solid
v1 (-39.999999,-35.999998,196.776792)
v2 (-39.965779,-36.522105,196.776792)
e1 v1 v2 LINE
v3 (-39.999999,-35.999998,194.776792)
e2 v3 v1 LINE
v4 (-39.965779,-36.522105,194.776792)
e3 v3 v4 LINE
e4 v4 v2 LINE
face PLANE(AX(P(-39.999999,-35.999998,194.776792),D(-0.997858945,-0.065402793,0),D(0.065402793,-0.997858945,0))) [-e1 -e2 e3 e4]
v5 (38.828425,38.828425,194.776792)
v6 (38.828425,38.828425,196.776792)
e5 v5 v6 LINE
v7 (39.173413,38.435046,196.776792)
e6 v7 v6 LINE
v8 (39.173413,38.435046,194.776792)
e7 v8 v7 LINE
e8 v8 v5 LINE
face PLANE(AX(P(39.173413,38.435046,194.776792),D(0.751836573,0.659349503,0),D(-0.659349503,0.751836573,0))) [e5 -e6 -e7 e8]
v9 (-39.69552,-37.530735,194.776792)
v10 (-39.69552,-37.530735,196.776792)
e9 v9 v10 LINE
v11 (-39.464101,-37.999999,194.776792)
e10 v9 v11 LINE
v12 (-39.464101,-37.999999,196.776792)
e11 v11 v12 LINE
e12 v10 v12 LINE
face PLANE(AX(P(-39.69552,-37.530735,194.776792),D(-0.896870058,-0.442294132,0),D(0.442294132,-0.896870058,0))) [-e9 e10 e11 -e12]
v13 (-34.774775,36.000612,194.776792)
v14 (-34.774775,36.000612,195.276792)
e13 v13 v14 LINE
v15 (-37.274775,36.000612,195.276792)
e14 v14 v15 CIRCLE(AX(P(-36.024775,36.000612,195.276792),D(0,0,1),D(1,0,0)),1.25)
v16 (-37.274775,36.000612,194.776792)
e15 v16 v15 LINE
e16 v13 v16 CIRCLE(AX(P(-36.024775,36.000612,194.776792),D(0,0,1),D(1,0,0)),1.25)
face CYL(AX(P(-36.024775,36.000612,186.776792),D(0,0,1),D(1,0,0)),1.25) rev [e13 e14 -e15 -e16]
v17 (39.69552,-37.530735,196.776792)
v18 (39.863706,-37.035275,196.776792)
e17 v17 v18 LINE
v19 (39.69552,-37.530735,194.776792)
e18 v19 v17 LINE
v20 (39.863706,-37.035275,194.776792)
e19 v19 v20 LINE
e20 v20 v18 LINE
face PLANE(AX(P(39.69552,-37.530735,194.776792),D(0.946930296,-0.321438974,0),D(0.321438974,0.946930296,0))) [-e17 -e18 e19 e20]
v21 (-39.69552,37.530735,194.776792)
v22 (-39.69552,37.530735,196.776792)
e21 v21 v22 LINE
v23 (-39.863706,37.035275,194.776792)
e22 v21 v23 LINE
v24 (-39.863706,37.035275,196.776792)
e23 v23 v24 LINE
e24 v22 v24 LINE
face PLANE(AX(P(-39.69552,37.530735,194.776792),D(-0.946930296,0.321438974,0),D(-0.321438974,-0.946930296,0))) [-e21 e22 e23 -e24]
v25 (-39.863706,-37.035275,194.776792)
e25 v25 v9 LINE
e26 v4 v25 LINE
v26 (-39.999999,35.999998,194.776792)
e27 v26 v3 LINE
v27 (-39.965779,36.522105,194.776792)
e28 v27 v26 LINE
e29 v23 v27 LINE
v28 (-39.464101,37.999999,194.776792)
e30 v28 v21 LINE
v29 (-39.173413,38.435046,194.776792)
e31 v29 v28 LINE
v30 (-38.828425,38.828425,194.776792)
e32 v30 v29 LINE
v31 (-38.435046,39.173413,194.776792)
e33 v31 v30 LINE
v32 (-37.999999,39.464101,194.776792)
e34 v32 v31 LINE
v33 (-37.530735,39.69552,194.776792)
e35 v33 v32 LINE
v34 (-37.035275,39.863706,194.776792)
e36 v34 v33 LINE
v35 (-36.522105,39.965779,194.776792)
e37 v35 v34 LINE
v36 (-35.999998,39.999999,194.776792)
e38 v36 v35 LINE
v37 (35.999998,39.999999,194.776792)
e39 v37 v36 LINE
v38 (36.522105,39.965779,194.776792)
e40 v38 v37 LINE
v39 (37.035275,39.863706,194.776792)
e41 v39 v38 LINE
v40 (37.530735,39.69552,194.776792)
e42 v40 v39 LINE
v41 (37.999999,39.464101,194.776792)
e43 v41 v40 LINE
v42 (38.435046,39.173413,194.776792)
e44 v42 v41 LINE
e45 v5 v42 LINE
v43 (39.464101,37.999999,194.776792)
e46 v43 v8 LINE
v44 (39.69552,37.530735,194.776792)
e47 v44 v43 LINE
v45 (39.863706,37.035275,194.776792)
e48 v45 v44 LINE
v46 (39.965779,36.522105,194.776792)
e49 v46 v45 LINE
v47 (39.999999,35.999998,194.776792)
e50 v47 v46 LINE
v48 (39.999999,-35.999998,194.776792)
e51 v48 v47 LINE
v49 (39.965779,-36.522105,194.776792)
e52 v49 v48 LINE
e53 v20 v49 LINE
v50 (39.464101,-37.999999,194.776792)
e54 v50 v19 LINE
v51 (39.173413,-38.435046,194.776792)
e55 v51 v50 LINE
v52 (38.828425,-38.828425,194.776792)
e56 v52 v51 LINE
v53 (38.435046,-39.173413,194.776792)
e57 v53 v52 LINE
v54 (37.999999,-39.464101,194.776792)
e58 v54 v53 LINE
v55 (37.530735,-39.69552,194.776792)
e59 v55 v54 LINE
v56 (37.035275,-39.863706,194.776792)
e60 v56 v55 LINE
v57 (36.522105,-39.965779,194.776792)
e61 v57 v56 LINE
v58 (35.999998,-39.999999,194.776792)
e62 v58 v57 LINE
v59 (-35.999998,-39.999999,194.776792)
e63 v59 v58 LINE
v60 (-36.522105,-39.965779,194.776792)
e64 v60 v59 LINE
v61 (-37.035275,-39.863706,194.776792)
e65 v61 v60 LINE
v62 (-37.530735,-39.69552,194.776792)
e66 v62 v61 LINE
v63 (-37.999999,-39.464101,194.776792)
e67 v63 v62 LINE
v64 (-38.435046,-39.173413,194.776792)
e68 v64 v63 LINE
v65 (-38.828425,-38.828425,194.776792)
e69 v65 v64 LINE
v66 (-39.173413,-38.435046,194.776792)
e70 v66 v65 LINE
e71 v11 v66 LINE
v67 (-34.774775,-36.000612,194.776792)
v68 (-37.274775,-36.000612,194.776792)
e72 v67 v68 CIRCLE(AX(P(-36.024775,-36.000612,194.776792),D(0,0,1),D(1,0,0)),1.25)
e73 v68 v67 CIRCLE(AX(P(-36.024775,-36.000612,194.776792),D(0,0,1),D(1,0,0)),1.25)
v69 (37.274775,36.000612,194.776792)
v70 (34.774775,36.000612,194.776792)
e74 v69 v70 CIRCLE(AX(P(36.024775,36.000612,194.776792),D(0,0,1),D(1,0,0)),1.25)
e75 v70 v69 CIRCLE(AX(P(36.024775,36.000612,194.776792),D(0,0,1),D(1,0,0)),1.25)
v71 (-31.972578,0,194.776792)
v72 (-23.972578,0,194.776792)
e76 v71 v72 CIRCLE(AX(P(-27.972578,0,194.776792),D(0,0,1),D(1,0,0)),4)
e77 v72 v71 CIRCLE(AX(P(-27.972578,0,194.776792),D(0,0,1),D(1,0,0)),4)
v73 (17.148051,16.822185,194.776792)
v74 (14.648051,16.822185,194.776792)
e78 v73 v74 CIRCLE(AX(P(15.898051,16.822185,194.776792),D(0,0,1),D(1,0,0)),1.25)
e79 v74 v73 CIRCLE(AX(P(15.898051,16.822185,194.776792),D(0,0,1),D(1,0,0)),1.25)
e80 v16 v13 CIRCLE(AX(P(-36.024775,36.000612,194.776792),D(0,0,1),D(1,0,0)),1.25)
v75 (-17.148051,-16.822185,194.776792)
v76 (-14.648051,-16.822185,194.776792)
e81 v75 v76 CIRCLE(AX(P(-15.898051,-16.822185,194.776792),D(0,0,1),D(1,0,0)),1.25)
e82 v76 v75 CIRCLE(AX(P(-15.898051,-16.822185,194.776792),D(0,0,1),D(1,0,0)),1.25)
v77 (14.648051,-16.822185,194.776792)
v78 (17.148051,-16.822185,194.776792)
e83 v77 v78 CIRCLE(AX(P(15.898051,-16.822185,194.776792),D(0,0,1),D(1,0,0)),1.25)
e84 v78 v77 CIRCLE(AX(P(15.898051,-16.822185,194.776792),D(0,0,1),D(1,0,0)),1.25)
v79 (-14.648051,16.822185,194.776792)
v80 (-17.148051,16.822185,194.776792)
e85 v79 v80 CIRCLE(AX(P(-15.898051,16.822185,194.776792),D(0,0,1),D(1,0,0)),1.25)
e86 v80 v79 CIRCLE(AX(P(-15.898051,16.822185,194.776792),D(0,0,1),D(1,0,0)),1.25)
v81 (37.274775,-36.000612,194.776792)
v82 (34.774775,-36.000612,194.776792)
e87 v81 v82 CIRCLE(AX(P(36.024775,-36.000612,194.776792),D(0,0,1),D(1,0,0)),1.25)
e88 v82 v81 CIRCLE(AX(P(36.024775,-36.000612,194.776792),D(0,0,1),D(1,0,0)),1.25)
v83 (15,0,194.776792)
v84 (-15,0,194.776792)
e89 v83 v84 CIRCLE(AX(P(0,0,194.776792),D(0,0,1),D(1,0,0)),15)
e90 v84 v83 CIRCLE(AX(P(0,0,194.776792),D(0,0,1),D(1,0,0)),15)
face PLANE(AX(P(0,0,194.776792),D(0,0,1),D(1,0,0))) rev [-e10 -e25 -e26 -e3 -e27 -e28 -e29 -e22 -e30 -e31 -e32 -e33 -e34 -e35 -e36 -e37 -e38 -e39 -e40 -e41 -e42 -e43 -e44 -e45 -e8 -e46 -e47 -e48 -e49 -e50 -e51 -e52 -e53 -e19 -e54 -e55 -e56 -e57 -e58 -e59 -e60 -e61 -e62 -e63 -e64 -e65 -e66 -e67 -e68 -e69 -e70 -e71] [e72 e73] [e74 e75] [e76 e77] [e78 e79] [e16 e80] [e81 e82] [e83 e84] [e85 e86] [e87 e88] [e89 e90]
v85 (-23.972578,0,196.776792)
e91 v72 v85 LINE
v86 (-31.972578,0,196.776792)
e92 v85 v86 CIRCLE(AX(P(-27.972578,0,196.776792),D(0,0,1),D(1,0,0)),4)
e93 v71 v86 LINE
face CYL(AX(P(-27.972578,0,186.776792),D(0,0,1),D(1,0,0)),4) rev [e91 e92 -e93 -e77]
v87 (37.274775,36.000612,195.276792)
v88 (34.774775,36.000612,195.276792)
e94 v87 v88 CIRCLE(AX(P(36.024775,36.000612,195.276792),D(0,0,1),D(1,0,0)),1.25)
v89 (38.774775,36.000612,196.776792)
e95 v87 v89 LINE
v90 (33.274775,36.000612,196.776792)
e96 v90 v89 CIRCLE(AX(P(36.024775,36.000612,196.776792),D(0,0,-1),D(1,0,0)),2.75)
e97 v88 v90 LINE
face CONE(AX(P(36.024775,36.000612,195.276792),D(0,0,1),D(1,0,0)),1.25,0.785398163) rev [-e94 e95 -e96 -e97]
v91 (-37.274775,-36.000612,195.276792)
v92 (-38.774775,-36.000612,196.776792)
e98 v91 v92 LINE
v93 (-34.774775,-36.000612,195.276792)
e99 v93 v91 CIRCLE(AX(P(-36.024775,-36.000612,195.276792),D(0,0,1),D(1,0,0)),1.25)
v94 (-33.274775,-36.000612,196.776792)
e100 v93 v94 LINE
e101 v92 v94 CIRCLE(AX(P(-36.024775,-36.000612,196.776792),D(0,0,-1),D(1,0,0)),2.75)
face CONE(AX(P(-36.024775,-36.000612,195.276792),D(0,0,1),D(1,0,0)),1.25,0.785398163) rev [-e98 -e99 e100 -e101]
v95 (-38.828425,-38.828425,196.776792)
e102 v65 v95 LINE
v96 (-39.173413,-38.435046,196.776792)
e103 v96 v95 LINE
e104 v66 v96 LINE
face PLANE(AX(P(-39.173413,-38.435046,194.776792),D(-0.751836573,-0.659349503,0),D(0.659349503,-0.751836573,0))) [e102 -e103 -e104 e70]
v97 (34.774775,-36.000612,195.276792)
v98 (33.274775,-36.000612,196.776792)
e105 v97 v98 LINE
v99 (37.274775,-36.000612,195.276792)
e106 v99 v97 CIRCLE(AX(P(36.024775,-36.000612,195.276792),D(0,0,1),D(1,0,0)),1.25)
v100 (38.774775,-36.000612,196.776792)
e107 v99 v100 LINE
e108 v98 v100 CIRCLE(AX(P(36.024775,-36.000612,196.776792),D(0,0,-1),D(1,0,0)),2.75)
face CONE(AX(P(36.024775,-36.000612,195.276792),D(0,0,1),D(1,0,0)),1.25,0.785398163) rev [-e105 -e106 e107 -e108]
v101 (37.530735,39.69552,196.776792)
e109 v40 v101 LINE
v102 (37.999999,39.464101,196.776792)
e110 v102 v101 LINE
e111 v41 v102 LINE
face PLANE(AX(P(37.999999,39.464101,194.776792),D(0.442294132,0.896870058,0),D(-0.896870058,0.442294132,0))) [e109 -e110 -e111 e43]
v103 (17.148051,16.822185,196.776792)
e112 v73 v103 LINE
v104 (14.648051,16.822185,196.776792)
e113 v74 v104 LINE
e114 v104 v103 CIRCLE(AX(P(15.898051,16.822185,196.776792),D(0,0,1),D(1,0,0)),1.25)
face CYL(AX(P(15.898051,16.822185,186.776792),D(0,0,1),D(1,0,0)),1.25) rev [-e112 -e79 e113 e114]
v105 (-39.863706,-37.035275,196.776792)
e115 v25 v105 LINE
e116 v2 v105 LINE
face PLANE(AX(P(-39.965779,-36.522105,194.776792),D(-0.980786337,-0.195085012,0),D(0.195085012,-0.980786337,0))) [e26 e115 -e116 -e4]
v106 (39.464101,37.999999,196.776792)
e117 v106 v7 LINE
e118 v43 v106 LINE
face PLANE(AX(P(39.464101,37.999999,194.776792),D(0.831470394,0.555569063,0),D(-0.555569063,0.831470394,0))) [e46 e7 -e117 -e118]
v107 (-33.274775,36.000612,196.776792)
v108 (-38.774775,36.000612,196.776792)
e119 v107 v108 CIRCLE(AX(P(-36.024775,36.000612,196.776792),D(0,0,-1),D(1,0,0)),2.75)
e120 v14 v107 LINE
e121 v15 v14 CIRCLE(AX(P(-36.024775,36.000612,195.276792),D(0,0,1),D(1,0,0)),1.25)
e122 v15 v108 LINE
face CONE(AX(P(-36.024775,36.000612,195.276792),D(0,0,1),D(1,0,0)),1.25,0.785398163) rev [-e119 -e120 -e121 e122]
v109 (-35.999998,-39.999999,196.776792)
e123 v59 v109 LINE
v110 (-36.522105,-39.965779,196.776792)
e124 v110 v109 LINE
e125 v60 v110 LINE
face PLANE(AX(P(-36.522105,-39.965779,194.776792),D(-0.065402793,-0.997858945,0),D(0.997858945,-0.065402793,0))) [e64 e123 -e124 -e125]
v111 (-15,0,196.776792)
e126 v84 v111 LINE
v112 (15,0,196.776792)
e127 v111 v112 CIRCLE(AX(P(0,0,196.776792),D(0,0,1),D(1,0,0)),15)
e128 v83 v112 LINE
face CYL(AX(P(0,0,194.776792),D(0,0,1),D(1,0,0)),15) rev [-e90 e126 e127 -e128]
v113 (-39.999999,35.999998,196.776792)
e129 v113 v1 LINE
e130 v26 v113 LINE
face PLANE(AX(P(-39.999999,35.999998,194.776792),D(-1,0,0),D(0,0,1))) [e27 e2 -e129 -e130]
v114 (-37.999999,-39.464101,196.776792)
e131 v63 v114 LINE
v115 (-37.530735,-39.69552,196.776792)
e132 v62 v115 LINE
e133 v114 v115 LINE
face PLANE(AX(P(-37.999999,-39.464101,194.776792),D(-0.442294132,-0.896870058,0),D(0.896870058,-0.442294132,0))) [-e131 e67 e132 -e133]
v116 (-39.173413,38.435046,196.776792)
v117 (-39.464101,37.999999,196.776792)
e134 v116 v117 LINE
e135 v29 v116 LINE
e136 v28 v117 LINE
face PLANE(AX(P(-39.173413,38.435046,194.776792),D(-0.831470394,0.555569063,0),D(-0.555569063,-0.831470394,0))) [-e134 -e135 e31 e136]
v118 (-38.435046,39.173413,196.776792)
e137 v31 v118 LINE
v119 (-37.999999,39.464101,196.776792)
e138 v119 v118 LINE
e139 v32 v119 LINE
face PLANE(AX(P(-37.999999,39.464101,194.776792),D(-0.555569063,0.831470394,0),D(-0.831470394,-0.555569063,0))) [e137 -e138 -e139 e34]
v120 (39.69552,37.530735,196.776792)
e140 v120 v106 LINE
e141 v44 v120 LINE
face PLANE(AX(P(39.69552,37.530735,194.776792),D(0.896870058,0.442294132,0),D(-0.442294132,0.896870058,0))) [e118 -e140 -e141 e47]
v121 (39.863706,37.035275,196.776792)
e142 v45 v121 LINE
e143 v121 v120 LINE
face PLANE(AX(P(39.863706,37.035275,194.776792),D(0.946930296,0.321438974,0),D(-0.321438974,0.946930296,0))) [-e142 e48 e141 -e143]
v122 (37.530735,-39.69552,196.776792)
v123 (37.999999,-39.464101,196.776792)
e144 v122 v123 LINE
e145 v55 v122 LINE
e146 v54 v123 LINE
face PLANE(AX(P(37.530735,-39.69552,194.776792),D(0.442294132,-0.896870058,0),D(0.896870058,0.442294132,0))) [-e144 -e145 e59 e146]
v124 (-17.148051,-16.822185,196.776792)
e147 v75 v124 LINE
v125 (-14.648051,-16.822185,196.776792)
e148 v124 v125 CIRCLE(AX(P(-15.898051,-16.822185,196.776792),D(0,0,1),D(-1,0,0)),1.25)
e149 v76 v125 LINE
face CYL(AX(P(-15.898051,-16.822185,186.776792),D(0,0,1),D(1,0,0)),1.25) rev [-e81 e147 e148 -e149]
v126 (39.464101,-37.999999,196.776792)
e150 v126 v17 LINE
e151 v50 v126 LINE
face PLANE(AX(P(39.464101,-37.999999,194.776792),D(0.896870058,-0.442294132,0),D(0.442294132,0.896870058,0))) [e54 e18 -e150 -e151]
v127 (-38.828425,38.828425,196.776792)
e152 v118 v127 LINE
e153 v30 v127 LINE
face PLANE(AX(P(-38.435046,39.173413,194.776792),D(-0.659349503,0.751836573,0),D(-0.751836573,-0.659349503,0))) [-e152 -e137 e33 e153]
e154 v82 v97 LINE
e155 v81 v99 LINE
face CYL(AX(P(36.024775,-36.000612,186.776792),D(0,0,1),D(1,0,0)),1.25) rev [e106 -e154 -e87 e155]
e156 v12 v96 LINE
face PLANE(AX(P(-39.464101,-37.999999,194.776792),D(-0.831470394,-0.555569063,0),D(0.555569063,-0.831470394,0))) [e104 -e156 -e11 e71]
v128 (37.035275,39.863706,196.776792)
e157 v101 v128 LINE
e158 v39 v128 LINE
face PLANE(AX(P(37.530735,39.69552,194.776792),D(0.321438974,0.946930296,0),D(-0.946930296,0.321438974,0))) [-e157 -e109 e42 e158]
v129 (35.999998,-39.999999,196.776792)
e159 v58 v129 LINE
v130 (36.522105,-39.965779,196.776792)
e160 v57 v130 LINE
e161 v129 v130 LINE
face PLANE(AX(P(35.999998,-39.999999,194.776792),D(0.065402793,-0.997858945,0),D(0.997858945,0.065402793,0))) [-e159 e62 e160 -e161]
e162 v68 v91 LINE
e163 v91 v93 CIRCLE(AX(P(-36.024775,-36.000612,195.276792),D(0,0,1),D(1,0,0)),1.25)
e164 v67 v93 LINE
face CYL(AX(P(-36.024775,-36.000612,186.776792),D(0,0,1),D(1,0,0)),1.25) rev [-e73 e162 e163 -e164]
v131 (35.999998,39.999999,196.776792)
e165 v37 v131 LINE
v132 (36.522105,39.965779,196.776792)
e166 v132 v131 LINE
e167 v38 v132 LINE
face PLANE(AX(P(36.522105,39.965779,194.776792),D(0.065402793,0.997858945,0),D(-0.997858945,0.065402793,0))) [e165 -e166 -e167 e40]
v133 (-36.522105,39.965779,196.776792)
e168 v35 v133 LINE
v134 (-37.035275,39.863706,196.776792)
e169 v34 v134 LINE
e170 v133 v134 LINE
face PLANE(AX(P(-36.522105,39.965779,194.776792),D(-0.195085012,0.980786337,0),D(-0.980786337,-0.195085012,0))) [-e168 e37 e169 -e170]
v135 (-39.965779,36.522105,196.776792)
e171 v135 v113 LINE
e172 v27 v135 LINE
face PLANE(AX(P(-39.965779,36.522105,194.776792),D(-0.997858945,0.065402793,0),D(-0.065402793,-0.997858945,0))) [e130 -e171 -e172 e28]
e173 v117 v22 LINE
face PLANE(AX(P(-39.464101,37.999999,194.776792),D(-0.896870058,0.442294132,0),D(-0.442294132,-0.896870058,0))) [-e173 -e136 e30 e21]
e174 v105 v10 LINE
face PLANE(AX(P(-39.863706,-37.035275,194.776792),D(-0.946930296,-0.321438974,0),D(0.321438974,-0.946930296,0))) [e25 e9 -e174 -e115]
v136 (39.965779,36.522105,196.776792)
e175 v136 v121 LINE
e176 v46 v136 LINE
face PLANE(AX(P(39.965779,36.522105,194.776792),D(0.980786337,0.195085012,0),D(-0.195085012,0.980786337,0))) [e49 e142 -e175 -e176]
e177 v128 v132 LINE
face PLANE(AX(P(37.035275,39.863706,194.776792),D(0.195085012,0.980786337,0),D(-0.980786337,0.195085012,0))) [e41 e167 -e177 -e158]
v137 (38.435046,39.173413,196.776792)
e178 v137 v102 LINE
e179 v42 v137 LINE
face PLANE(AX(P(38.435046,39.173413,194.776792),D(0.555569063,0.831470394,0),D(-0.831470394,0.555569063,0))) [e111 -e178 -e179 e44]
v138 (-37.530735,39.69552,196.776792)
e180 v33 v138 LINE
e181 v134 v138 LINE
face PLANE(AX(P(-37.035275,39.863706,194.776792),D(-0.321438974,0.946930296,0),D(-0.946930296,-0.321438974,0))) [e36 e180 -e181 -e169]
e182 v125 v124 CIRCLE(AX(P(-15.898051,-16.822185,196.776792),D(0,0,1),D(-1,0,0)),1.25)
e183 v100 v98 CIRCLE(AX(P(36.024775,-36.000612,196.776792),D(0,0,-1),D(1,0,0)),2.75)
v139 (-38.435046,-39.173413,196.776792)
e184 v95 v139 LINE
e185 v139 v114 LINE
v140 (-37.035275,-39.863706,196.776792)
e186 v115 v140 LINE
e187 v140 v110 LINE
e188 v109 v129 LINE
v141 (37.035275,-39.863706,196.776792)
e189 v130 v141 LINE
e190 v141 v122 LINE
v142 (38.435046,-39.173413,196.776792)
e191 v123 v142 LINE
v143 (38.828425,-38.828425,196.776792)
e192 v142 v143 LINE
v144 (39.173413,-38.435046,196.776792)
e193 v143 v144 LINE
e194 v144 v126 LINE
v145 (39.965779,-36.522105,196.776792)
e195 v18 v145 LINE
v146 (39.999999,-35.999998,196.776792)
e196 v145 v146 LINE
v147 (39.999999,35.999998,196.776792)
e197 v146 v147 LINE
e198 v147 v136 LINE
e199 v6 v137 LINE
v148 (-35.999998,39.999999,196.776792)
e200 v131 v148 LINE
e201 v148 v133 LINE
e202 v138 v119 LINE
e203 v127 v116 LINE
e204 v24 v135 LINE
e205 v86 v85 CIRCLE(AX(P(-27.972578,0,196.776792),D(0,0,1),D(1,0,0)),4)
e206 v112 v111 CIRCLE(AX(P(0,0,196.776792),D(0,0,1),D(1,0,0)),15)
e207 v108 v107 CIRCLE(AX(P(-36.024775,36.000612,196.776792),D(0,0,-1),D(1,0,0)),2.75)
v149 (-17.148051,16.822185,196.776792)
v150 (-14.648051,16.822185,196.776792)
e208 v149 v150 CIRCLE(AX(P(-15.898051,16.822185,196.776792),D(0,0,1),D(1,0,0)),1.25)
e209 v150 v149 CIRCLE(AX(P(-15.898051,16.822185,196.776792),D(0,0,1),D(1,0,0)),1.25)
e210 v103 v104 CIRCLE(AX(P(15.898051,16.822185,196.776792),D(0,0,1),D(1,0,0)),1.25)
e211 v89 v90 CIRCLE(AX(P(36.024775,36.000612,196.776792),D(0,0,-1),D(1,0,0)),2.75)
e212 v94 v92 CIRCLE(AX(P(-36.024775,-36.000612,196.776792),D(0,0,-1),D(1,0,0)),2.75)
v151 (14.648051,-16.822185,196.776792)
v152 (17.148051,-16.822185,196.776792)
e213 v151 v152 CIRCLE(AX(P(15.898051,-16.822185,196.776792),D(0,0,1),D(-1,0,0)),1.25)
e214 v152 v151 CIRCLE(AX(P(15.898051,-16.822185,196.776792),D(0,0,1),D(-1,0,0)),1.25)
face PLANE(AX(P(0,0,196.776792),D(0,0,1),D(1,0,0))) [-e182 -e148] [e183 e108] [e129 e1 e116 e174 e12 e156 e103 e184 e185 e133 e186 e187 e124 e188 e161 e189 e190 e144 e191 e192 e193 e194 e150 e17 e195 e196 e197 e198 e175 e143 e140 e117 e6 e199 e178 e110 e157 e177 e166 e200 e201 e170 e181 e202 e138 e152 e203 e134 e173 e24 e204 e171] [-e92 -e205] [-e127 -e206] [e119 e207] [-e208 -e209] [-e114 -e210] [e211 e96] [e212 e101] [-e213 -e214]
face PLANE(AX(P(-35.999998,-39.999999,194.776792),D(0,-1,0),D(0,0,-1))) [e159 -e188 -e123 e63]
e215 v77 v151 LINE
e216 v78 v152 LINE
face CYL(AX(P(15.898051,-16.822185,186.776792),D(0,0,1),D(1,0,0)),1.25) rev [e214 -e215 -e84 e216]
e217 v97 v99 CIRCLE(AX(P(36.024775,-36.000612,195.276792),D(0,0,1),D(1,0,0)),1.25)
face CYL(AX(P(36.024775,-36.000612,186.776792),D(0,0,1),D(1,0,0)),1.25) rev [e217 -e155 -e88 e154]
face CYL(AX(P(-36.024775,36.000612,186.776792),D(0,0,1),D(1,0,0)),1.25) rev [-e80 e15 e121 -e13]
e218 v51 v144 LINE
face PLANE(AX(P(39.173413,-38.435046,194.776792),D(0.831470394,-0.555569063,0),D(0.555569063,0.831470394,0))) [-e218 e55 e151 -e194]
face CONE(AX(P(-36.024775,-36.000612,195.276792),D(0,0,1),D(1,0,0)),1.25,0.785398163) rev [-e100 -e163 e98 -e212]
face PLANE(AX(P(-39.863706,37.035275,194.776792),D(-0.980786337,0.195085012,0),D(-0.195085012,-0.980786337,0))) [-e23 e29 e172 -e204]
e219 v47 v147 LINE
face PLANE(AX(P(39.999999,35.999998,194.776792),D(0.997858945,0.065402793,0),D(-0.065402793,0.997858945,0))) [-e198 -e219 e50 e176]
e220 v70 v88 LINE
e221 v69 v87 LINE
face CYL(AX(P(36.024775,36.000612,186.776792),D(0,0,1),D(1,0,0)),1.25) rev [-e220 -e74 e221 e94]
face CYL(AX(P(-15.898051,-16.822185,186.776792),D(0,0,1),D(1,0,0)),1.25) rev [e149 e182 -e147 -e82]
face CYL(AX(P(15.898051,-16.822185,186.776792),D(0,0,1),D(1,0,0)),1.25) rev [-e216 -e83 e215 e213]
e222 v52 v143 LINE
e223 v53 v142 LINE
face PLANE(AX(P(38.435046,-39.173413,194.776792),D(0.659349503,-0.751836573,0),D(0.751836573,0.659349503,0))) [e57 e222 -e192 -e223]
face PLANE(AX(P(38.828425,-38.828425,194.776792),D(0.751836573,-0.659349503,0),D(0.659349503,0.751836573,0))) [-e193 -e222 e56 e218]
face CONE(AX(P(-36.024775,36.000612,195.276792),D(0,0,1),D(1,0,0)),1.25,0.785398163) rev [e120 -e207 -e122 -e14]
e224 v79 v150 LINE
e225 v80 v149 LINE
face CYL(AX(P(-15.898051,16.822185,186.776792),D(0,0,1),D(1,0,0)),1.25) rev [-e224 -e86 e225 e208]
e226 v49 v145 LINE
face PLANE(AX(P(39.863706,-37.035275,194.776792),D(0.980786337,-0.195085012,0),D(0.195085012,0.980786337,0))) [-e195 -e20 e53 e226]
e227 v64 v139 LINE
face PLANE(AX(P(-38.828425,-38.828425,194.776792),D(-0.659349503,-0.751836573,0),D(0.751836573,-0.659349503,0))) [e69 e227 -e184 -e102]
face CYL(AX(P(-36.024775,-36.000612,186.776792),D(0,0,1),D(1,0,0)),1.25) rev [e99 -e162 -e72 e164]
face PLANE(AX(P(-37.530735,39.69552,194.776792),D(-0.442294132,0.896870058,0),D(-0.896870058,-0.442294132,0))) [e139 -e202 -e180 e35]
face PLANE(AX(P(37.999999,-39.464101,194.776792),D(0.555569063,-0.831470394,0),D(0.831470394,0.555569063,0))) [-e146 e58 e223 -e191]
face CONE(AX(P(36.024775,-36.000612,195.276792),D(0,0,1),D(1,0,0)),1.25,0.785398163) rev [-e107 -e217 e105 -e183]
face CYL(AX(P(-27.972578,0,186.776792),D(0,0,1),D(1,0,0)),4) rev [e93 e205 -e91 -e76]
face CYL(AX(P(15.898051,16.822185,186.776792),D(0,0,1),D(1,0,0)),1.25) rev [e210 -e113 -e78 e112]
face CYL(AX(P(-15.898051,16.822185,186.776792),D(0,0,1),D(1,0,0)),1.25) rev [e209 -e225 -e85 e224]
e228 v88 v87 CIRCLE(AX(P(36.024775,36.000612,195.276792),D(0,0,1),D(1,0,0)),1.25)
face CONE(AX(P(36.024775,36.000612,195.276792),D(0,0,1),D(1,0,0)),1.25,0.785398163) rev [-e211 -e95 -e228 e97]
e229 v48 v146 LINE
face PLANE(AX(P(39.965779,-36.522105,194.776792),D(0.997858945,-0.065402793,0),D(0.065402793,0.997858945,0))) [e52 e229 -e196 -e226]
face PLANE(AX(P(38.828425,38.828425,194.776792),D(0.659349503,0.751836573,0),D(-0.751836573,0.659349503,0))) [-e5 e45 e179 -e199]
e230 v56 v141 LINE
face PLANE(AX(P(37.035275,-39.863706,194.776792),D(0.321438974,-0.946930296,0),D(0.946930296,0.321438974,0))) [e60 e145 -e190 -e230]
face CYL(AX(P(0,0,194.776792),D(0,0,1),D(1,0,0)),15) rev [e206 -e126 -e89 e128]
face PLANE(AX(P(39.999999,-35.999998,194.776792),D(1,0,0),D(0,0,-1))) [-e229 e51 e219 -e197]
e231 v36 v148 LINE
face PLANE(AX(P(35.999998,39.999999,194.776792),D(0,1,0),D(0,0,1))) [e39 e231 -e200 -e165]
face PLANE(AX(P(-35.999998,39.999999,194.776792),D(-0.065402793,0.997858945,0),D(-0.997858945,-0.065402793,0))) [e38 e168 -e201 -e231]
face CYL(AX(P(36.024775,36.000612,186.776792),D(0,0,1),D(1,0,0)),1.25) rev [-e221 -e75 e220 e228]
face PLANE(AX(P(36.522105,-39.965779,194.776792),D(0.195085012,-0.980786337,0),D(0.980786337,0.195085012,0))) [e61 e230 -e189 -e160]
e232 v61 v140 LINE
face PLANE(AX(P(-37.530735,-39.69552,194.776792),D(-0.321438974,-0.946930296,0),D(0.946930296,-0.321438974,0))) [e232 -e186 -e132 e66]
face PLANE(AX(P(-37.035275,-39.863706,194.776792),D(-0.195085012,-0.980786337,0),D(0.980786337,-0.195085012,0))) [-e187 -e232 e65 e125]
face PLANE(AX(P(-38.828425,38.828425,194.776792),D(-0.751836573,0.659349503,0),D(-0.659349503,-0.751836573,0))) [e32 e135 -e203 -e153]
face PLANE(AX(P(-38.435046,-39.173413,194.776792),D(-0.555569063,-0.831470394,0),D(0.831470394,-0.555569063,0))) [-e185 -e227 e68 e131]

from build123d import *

# Parameters (mm, degrees)
BOSS_EXTRUDE1_DEPTH     = 2
CUT_EXTRUDE1_DEPTH      = 57.603885529
CUT_EXTRUDE1_DEPTH_BACK = 57.603885529
SKETCH2_R               = 15
SKETCH3_R               = 4
CUT_EXTRUDE2_DEPTH      = 10
SKETCH4_R               = 1.25
CUT_EXTRUDE3_DEPTH      = 10
SKETCH5_R               = 2
CUT_EXTRUDE4_DEPTH      = 10
MOVE_FACE1_BY           = 0.75
MOVE_FACE1_2_BY         = 0.75
MOVE_FACE1_3_BY         = 0.75
MOVE_FACE1_4_BY         = 0.75
CHAMFER1_SIZE           = 1.5


with BuildPart() as part:
    # Sketch1 → Boss-Extrude1 (new body)
    with BuildSketch(Plane.XY.offset(196.776792407)):
        Polygon((-39.999999106, -35.99999845), (-39.965778589, -36.522105336), (-39.863705635, -37.035275251), (-39.695519954, -37.530735135), (-39.464101195, -37.999998778), (-39.173413068, -38.43504563), (-38.828425109, -38.828425109), (-38.43504563, -39.173413068), (-37.999998778, -39.464101195), (-37.530735135, -39.695519954), (-37.035275251, -39.863705635), (-36.522105336, -39.965778589), (-35.99999845, -39.999999106), (35.99999845, -39.999999106), (36.522105336, -39.965778589), (37.035275251, -39.863705635), (37.530735135, -39.695519954), (37.999998778, -39.464101195), (38.43504563, -39.173413068), (38.828425109, -38.828425109), (39.173413068, -38.43504563), (39.464101195, -37.999998778), (39.695519954, -37.530735135), (39.863705635, -37.035275251), (39.965778589, -36.522105336), (39.999999106, -35.99999845), (39.999999106, 35.99999845), (39.965778589, 36.522105336), (39.863705635, 37.035275251), (39.695519954, 37.530735135), (39.464101195, 37.999998778), (39.173413068, 38.43504563), (38.828425109, 38.828425109), (38.43504563, 39.173413068), (37.999998778, 39.464101195), (37.530735135, 39.695519954), (37.035275251, 39.863705635), (36.522105336, 39.965778589), (35.99999845, 39.999999106), (-35.99999845, 39.999999106), (-36.522105336, 39.965778589), (-37.035275251, 39.863705635), (-37.530735135, 39.695519954), (-37.999998778, 39.464101195), (-38.43504563, 39.173413068), (-38.828425109, 38.828425109), (-39.173413068, 38.43504563), (-39.464101195, 37.999998778), (-39.695519954, 37.530735135), (-39.863705635, 37.035275251), (-39.965778589, 36.522105336), (-39.999999106, 35.99999845), align=None)
        Polygon((-37.448886782, -36.388229579), (-37.50000149, -35.99999845), (-37.448886782, -35.611771047), (-37.29903698, -35.250000656), (-37.060663104, -34.939337522), (-36.74999997, -34.700963646), (-36.388229579, -34.551113844), (-35.99999845, -34.499999136), (-35.611771047, -34.551113844), (-35.250000656, -34.700963646), (-34.939337522, -34.939337522), (-34.700963646, -35.250000656), (-34.551113844, -35.611771047), (-34.499999136, -35.99999845), (-34.551113844, -36.388229579), (-34.700963646, -36.74999997), (-34.939337522, -37.060663104), (-35.250000656, -37.29903698), (-35.611771047, -37.448886782), (-35.99999845, -37.50000149), (-36.388229579, -37.448886782), (-36.74999997, -37.29903698), (-37.060663104, -37.060663104), (-37.29903698, -36.74999997), align=None, mode=Mode.SUBTRACT)
        Polygon((-37.448886782, 35.611771047), (-37.50000149, 35.99999845), (-37.448886782, 36.388229579), (-37.29903698, 36.74999997), (-37.060663104, 37.060663104), (-36.74999997, 37.29903698), (-36.388229579, 37.448886782), (-35.99999845, 37.50000149), (-35.611771047, 37.448886782), (-35.250000656, 37.29903698), (-34.939337522, 37.060663104), (-34.700963646, 36.74999997), (-34.551113844, 36.388229579), (-34.499999136, 35.99999845), (-34.551113844, 35.611771047), (-34.700963646, 35.250000656), (-34.939337522, 34.939337522), (-35.250000656, 34.700963646), (-35.611771047, 34.551113844), (-35.99999845, 34.499999136), (-36.388229579, 34.551113844), (-36.74999997, 34.700963646), (-37.060663104, 34.939337522), (-37.29903698, 35.250000656), align=None, mode=Mode.SUBTRACT)
        Polygon((34.787815064, -36.8835181), (34.600444138, -36.539677531), (34.508455545, -36.159053445), (34.518111497, -35.767596215), (34.628756344, -35.391975194), (34.832850099, -35.057790577), (35.116482526, -34.787815064), (35.460323095, -34.600444138), (35.840947181, -34.508455545), (36.232404411, -34.518111497), (36.608025432, -34.628756344), (36.942210048, -34.832850099), (37.212185562, -35.116482526), (37.399556488, -35.460323095), (37.491541356, -35.840947181), (37.481926863, -36.232448961), (37.371270724, -36.608066656), (37.167163198, -36.942245137), (36.88352638, -37.212212123), (36.539680178, -37.399572712), (36.159053327, -37.491546138), (35.99999845, -37.48762235), (35.767596215, -37.481889129), (35.391975194, -37.371244282), (35.057790577, -37.167146802), align=None, mode=Mode.SUBTRACT)
        Polygon((34.551113844, 35.611771047), (34.499999136, 35.99999845), (34.551113844, 36.388229579), (34.700963646, 36.74999997), (34.939337522, 37.060663104), (35.250000656, 37.29903698), (35.611771047, 37.448886782), (35.99999845, 37.50000149), (36.388229579, 37.448886782), (36.74999997, 37.29903698), (37.060663104, 37.060663104), (37.29903698, 36.74999997), (37.448886782, 36.388229579), (37.50000149, 35.99999845), (37.448886782, 35.611771047), (37.29903698, 35.250000656), (37.060663104, 34.939337522), (36.74999997, 34.700963646), (36.388229579, 34.551113844), (35.99999845, 34.499999136), (35.611771047, 34.551113844), (35.250000656, 34.700963646), (34.939337522, 34.939337522), (34.700963646, 35.250000656), align=None, mode=Mode.SUBTRACT)
    extrude(amount=-BOSS_EXTRUDE1_DEPTH)

    # Sketch2 → Cut-Extrude1 (cut, two sides: drawn at the far end of the back side and taken through both)
    with BuildSketch(Plane.XY.offset(196.776792407).offset(-CUT_EXTRUDE1_DEPTH_BACK)):
        Circle(SKETCH2_R)
    extrude(amount=CUT_EXTRUDE1_DEPTH + CUT_EXTRUDE1_DEPTH_BACK, mode=Mode.SUBTRACT)

    # Sketch3 → Cut-Extrude2 (cut)
    with BuildSketch(Plane.XY.offset(196.776792407)):
        with Locations((-27.97257793, 0)):
            Circle(SKETCH3_R)
    extrude(amount=-CUT_EXTRUDE2_DEPTH, mode=Mode.SUBTRACT)

    # Sketch4 → Cut-Extrude3 (cut)
    with BuildSketch(Plane.XY.offset(196.776792407)):
        with Locations((15.898051321, 16.822185345)):
            Circle(SKETCH4_R)
        with Locations((-15.898051321, 16.822185345)):
            Circle(SKETCH4_R)
        with Locations((-15.898051321, -16.822185345)):
            Circle(SKETCH4_R)
        with Locations((15.898051321, -16.822185345)):
            Circle(SKETCH4_R)
    extrude(amount=-CUT_EXTRUDE3_DEPTH, mode=Mode.SUBTRACT)

    # Sketch5 → Cut-Extrude4 (cut)
    with BuildSketch(Plane.XY.offset(196.776792407)):
        with Locations((36.024774728, -36.000611748)):
            Circle(SKETCH5_R)
        with Locations((-36.024774728, -36.000611748)):
            Circle(SKETCH5_R)
        with Locations((-36.024774728, 36.000611748)):
            Circle(SKETCH5_R)
        with Locations((36.024774728, 36.000611748)):
            Circle(SKETCH5_R)
    extrude(amount=-CUT_EXTRUDE4_DEPTH, mode=Mode.SUBTRACT)

    # Move Face1: a curved face moved outward by 0.75
    add(Solid.thicken(part.faces().sort_by_distance((34.024774728, 36.000611748, 195.776792407))[0], MOVE_FACE1_BY))

    # Move Face1 2: a curved face moved outward by 0.75
    add(Solid.thicken(part.faces().sort_by_distance((-38.024774728, 36.000611748, 195.776792407))[0], MOVE_FACE1_2_BY))

    # Move Face1 3: a curved face moved outward by 0.75
    add(Solid.thicken(part.faces().sort_by_distance((-38.024774728, -36.000611748, 195.776792407))[0], MOVE_FACE1_3_BY))

    # Move Face1 4: a curved face moved outward by 0.75
    add(Solid.thicken(part.faces().sort_by_distance((34.024774728, -36.000611748, 195.776792407))[0], MOVE_FACE1_4_BY))

    # Chamfer1
    chamfer1_edges = [part.edges().sort_by_distance(p)[0] for p in [
        (34.774774728, 36.000611748, 196.776792407),
        (-37.274774728, 36.000611748, 196.776792407),
        (-37.274774728, -36.000611748, 196.776792407),
        (34.774774728, -36.000611748, 196.776792407),
    ]]
    chamfer(chamfer1_edges, length=CHAMFER1_SIZE)


solid = part.part
